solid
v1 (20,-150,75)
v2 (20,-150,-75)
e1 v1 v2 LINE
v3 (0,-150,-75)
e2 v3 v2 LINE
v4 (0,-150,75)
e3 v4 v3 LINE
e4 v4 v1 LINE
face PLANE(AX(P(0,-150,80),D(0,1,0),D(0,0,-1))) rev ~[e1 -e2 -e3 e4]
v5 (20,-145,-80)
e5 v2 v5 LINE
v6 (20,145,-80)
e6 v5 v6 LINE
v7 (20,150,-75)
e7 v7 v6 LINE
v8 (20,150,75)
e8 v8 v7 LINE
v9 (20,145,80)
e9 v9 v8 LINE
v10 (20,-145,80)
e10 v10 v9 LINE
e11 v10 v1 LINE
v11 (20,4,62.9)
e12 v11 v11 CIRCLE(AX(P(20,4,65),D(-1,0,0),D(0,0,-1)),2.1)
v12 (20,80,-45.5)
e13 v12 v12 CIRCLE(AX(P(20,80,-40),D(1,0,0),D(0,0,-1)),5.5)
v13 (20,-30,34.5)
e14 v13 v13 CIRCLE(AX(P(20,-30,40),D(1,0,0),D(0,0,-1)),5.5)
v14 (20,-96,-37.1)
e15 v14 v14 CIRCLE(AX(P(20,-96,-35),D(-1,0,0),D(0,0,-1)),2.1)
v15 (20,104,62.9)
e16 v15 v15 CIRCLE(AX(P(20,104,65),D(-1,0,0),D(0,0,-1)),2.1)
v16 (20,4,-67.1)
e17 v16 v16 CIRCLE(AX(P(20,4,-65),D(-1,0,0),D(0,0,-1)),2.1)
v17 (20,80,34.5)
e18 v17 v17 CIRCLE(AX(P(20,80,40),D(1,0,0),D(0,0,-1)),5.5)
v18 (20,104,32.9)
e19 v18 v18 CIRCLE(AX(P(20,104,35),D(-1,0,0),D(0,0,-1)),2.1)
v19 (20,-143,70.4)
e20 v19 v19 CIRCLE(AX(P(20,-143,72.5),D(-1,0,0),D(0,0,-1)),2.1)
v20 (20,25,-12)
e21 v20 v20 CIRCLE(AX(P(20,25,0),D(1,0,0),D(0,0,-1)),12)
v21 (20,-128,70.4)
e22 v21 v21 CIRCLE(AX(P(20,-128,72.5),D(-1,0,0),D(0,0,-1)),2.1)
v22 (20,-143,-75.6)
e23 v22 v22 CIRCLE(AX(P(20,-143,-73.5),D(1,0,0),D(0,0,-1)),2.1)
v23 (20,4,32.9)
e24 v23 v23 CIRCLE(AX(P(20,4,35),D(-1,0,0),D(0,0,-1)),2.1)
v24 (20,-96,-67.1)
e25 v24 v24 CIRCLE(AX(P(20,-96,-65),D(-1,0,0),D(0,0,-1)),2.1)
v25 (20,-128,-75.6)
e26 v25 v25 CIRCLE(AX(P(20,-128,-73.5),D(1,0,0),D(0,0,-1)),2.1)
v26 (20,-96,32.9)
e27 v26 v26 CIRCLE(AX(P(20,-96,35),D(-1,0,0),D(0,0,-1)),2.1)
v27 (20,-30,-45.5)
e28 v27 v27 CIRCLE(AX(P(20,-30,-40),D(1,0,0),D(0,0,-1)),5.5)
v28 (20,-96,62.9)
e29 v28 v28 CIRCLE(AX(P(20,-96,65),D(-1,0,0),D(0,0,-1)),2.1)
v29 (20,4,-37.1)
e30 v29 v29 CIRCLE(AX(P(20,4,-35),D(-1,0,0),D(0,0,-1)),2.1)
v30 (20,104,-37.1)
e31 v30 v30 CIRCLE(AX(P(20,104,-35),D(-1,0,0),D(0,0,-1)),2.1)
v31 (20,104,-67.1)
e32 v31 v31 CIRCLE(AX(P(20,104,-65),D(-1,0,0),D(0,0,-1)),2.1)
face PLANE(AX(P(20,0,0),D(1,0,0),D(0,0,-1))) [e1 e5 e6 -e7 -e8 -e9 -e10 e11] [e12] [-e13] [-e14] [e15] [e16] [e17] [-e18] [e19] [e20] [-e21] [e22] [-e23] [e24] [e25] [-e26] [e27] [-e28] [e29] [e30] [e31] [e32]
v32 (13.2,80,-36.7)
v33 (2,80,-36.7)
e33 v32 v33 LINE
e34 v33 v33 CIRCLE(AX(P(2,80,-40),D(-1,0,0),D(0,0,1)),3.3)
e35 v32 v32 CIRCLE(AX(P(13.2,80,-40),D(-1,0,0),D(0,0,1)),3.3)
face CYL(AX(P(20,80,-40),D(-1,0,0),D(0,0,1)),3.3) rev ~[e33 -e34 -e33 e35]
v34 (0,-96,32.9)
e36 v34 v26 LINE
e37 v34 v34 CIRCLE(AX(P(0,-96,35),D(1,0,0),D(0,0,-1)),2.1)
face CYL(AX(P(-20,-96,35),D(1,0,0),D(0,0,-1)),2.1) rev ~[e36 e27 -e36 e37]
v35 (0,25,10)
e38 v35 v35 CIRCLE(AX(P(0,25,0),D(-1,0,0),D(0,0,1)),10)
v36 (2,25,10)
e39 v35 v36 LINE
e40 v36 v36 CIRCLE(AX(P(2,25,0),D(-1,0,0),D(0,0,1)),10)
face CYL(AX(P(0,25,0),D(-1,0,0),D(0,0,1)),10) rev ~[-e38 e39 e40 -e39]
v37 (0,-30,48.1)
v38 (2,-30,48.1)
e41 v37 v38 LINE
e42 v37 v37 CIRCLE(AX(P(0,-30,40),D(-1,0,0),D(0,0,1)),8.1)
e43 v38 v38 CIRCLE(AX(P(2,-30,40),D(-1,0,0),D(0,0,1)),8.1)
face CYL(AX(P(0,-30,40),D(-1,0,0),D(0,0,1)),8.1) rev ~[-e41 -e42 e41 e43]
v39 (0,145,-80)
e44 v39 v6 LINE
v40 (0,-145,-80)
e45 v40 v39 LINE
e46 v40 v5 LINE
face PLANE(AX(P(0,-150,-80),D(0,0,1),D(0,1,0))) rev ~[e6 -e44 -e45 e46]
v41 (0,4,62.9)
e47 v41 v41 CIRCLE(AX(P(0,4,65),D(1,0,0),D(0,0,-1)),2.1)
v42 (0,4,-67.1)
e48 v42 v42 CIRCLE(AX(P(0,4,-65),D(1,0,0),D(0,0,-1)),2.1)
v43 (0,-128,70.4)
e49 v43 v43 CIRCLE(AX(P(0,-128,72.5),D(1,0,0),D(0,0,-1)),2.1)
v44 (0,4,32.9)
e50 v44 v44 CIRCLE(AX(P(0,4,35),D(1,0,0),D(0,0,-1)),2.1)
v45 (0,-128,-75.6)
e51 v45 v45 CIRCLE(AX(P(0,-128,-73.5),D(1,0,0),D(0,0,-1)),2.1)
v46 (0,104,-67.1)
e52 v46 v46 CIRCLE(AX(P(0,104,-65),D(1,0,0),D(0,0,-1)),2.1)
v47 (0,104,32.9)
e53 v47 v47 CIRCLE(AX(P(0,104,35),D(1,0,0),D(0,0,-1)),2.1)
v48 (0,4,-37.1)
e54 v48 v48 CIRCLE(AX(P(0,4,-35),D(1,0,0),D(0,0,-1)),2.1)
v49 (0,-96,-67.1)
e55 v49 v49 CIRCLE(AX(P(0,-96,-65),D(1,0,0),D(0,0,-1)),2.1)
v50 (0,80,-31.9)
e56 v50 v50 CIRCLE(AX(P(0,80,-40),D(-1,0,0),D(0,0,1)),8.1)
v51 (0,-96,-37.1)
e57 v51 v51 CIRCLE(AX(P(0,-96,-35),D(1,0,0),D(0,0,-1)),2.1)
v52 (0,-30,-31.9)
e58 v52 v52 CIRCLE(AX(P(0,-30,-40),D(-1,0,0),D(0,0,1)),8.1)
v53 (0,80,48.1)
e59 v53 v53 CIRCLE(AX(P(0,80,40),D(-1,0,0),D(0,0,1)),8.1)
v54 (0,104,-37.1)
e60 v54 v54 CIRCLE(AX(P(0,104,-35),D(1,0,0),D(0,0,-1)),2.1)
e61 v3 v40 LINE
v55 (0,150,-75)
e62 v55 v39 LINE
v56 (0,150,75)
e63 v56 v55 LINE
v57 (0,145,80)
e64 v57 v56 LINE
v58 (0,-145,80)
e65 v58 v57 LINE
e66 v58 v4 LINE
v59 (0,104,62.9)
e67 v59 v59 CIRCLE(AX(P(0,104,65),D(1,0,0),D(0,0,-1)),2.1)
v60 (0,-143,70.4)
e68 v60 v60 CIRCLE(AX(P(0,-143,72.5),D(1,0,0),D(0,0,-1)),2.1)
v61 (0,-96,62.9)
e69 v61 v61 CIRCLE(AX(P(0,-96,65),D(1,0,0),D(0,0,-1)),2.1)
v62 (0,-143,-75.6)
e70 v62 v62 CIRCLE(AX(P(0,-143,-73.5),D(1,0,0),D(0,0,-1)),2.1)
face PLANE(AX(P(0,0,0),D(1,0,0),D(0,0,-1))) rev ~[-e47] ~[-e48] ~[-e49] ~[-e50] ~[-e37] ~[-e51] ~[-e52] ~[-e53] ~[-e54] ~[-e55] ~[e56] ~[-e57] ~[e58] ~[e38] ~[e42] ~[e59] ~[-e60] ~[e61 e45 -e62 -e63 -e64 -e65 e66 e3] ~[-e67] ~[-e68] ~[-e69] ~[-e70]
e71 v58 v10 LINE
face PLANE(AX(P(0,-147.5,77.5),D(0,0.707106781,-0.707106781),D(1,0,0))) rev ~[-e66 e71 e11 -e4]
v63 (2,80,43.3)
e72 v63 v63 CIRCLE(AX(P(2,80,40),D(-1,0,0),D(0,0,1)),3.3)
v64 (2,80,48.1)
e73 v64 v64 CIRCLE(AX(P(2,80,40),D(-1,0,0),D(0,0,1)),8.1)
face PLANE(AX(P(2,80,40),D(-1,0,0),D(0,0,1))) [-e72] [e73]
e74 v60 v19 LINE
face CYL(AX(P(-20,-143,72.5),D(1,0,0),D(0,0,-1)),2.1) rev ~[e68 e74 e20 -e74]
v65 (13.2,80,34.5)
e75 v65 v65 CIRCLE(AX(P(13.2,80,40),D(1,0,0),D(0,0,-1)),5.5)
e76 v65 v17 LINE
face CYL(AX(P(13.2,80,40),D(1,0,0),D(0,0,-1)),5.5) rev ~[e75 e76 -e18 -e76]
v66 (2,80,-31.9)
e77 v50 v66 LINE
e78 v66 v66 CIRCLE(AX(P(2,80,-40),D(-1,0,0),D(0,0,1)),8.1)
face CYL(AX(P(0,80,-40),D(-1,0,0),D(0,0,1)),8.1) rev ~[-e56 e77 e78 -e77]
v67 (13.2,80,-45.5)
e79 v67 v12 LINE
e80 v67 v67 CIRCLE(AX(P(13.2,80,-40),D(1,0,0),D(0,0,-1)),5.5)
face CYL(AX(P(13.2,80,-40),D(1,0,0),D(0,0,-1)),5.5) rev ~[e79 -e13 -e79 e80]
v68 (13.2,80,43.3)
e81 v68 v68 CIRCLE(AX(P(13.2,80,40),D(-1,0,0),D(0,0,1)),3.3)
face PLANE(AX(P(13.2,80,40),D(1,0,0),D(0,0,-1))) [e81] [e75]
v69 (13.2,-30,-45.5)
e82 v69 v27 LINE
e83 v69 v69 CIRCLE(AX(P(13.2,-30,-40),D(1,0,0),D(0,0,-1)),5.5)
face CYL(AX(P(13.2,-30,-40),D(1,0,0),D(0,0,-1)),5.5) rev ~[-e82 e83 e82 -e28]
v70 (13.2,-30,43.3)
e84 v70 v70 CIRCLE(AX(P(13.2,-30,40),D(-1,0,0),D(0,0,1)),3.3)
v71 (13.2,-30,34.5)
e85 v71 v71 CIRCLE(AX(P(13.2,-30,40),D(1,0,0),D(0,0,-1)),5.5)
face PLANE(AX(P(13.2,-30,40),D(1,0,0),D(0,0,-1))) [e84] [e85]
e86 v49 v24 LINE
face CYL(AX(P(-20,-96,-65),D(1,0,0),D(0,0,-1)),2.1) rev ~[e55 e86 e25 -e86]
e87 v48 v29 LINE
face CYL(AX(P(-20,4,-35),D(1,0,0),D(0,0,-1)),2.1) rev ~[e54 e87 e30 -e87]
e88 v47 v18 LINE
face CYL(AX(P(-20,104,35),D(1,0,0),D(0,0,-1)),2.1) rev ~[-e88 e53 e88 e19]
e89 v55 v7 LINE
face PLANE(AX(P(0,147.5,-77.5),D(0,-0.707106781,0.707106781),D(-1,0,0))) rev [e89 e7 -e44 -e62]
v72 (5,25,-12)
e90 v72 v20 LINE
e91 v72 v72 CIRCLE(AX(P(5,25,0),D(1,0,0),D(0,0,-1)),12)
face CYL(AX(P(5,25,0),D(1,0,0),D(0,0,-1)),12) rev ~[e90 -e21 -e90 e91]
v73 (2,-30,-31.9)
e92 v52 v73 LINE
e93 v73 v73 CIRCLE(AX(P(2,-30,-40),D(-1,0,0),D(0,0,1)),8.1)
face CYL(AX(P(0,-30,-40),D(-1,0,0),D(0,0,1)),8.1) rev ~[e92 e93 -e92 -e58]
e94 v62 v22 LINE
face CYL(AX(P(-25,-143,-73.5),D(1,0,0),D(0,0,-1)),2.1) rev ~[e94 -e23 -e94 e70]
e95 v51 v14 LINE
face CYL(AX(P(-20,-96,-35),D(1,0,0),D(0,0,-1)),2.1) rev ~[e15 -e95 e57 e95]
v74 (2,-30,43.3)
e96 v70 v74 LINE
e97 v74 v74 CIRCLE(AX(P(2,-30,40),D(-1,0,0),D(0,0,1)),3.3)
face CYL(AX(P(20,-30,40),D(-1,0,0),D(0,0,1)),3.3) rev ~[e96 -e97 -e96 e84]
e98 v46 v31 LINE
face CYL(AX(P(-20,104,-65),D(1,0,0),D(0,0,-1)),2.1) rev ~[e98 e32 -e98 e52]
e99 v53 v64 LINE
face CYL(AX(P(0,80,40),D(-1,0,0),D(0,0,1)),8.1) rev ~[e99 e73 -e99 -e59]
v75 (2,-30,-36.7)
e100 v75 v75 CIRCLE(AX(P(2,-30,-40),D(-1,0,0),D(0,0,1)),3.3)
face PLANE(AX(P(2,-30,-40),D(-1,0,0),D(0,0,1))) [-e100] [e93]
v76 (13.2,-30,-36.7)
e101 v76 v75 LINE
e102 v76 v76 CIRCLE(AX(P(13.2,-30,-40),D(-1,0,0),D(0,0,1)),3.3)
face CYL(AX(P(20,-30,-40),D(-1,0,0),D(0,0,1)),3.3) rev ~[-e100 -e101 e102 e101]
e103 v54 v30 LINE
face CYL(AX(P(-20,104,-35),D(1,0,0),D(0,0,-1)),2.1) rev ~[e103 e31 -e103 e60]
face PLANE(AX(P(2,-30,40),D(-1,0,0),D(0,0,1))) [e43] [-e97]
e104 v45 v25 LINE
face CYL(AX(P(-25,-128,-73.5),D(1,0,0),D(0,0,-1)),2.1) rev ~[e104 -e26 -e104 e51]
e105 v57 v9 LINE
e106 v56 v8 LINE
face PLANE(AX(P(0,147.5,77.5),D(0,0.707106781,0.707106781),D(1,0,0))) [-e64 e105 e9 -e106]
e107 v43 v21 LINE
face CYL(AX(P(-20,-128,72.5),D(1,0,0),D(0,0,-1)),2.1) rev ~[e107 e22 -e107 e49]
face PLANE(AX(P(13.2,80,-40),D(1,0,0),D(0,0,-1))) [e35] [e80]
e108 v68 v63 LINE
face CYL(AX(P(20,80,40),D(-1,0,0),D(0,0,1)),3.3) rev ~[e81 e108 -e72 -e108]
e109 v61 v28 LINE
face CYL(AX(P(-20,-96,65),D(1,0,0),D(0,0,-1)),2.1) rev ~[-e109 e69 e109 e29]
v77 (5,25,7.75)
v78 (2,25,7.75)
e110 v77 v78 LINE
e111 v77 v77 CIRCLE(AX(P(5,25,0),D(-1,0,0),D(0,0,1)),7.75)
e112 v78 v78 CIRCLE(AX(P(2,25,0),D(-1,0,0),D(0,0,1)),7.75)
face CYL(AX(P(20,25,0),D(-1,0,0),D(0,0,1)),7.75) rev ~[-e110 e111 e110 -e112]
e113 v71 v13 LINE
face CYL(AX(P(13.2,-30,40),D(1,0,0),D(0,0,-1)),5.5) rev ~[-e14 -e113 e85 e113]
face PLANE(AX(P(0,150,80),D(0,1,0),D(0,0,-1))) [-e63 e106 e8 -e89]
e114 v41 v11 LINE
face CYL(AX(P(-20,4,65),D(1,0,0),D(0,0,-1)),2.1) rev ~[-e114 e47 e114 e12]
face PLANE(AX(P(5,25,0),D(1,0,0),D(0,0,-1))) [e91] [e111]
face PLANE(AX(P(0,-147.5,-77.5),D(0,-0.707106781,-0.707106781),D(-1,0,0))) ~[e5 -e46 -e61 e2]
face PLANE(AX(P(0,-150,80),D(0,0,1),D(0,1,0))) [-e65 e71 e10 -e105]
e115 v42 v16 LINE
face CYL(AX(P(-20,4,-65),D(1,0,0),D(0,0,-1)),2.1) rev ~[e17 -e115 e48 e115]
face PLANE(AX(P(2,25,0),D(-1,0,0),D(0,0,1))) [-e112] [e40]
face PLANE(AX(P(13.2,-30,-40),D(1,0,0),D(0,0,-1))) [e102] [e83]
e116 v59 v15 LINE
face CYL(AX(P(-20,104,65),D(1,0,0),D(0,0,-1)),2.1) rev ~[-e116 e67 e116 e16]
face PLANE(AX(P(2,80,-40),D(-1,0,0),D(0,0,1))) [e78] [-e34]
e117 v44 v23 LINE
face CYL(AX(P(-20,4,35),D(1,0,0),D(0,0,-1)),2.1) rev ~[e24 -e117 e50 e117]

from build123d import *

# Parameters (mm, degrees)
SKETCH_1_W                = 160
SKETCH_1_H                = 300
EXTRUDE_1_DEPTH           = 20
HOLE_WIZARD_1_D           = 15.5
HOLE_WIZARD_1_DEPTH       = 25
HOLE_WIZARD_1_CBORE_D     = 24
HOLE_WIZARD_1_CBORE_DEPTH = 15
HOLE_WIZARD_1_TIP         = 4.656669797
CHAMFER_1_SIZE            = 5
HOLE_WIZARD_0_D           = 6.6
HOLE_WIZARD_0_DEPTH       = 25
HOLE_WIZARD_0_CBORE_D     = 11
HOLE_WIZARD_0_CBORE_DEPTH = 6.8
HOLE_WIZARD_0_TIP         = 1.982840043
SKETCH_6_R                = 8.1
SKETCH_6_R_2              = 10
CUT_EXTRUDE_1_DEPTH       = 2
HOLE_WIZARD_M5_1_D        = 4.2
HOLE_WIZARD_M5_1_DEPTH    = 20
HOLE_WIZARD_M5_1_TIP      = 1.2618073
HOLE_WIZARD_M5_2_D        = 4.2
HOLE_WIZARD_M5_2_DEPTH    = 20
HOLE_WIZARD_M5_2_TIP      = 1.2618073
HOLE_WIZARD_M5_3_D        = 4.2
HOLE_WIZARD_M5_3_DEPTH    = 25
HOLE_WIZARD_M5_3_TIP      = 1.2618073


with BuildPart() as part:
    # 草图1 → 凸台-拉伸1 (new body)
    with BuildSketch(Plane(origin=(0, 0, 0), x_dir=(0, 0, -1), z_dir=(1, 0, 0))):
        Rectangle(SKETCH_1_W, SKETCH_1_H)
    extrude(amount=EXTRUDE_1_DEPTH)

    # 打孔尺寸(%根据)内六角圆柱头螺钉的类型1
    with Locations(Plane(origin=(20, 0, 0), x_dir=(0, 0, -1), z_dir=(1, 0, 0))):
        with Locations((0, 25)):
            CounterBoreHole(HOLE_WIZARD_1_D / 2, HOLE_WIZARD_1_CBORE_D / 2, HOLE_WIZARD_1_CBORE_DEPTH, depth=HOLE_WIZARD_1_DEPTH)
            with Locations((0, 0, -(HOLE_WIZARD_1_DEPTH + HOLE_WIZARD_1_TIP / 2))):  # 118° drill point
                Cone(0, HOLE_WIZARD_1_D / 2, HOLE_WIZARD_1_TIP, mode=Mode.SUBTRACT)

    # 倒角1
    chamfer_1_edges = [part.edges().sort_by_distance(p)[0] for p in [
        (10, -150, -80),
        (10, -150, 80),
        (10, 150, 80),
        (10, 150, -80),
    ]]
    chamfer(chamfer_1_edges, length=CHAMFER_1_SIZE)

    # 打孔尺寸(%根据)内六角圆柱头螺钉的类型0
    with Locations(Plane(origin=(20, 0, 0), x_dir=(0, 0, -1), z_dir=(1, 0, 0))):
        with Locations((40, -30), (40, 80), (-40, -30), (-40, 80)):
            CounterBoreHole(HOLE_WIZARD_0_D / 2, HOLE_WIZARD_0_CBORE_D / 2, HOLE_WIZARD_0_CBORE_DEPTH, depth=HOLE_WIZARD_0_DEPTH)
            with Locations((0, 0, -(HOLE_WIZARD_0_DEPTH + HOLE_WIZARD_0_TIP / 2))):  # 118° drill point
                Cone(0, HOLE_WIZARD_0_D / 2, HOLE_WIZARD_0_TIP, mode=Mode.SUBTRACT)

    # 草图6 → 切除-拉伸1 (cut)
    with BuildSketch(Plane.ZY):
        with Locations((-40, 80)):
            Circle(SKETCH_6_R)
        with Locations((-40, -30)):
            Circle(SKETCH_6_R)
        with Locations((0, 25)):
            Circle(SKETCH_6_R_2)
        with Locations((40, -30)):
            Circle(SKETCH_6_R)
        with Locations((40, 80)):
            Circle(SKETCH_6_R)
    extrude(amount=-CUT_EXTRUDE_1_DEPTH, mode=Mode.SUBTRACT)

    # M5 螺纹孔1
    with Locations(Plane.ZY):
        with Locations((65, -96), (35, -96), (65, 4), (35, 4), (65, 104), (35, 104), (-35, 104), (-65, 104), (-35, 4), (-65, 4), (-35, -96), (-65, -96)):
            Hole(HOLE_WIZARD_M5_1_D / 2, depth=HOLE_WIZARD_M5_1_DEPTH)
            with Locations((0, 0, -(HOLE_WIZARD_M5_1_DEPTH + HOLE_WIZARD_M5_1_TIP / 2))):  # 118° drill point
                Cone(0, HOLE_WIZARD_M5_1_D / 2, HOLE_WIZARD_M5_1_TIP, mode=Mode.SUBTRACT)

    # M5 螺纹孔2
    with Locations(Plane.ZY):
        with Locations((72.5, -143), (72.5, -128)):
            Hole(HOLE_WIZARD_M5_2_D / 2, depth=HOLE_WIZARD_M5_2_DEPTH)
            with Locations((0, 0, -(HOLE_WIZARD_M5_2_DEPTH + HOLE_WIZARD_M5_2_TIP / 2))):  # 118° drill point
                Cone(0, HOLE_WIZARD_M5_2_D / 2, HOLE_WIZARD_M5_2_TIP, mode=Mode.SUBTRACT)

    # M5 螺纹孔3
    with Locations(Plane.ZY):
        with Locations((-73.5, -143), (-73.5, -128)):
            Hole(HOLE_WIZARD_M5_3_D / 2, depth=HOLE_WIZARD_M5_3_DEPTH)
            with Locations((0, 0, -(HOLE_WIZARD_M5_3_DEPTH + HOLE_WIZARD_M5_3_TIP / 2))):  # 118° drill point
                Cone(0, HOLE_WIZARD_M5_3_D / 2, HOLE_WIZARD_M5_3_TIP, mode=Mode.SUBTRACT)


solid = part.part
